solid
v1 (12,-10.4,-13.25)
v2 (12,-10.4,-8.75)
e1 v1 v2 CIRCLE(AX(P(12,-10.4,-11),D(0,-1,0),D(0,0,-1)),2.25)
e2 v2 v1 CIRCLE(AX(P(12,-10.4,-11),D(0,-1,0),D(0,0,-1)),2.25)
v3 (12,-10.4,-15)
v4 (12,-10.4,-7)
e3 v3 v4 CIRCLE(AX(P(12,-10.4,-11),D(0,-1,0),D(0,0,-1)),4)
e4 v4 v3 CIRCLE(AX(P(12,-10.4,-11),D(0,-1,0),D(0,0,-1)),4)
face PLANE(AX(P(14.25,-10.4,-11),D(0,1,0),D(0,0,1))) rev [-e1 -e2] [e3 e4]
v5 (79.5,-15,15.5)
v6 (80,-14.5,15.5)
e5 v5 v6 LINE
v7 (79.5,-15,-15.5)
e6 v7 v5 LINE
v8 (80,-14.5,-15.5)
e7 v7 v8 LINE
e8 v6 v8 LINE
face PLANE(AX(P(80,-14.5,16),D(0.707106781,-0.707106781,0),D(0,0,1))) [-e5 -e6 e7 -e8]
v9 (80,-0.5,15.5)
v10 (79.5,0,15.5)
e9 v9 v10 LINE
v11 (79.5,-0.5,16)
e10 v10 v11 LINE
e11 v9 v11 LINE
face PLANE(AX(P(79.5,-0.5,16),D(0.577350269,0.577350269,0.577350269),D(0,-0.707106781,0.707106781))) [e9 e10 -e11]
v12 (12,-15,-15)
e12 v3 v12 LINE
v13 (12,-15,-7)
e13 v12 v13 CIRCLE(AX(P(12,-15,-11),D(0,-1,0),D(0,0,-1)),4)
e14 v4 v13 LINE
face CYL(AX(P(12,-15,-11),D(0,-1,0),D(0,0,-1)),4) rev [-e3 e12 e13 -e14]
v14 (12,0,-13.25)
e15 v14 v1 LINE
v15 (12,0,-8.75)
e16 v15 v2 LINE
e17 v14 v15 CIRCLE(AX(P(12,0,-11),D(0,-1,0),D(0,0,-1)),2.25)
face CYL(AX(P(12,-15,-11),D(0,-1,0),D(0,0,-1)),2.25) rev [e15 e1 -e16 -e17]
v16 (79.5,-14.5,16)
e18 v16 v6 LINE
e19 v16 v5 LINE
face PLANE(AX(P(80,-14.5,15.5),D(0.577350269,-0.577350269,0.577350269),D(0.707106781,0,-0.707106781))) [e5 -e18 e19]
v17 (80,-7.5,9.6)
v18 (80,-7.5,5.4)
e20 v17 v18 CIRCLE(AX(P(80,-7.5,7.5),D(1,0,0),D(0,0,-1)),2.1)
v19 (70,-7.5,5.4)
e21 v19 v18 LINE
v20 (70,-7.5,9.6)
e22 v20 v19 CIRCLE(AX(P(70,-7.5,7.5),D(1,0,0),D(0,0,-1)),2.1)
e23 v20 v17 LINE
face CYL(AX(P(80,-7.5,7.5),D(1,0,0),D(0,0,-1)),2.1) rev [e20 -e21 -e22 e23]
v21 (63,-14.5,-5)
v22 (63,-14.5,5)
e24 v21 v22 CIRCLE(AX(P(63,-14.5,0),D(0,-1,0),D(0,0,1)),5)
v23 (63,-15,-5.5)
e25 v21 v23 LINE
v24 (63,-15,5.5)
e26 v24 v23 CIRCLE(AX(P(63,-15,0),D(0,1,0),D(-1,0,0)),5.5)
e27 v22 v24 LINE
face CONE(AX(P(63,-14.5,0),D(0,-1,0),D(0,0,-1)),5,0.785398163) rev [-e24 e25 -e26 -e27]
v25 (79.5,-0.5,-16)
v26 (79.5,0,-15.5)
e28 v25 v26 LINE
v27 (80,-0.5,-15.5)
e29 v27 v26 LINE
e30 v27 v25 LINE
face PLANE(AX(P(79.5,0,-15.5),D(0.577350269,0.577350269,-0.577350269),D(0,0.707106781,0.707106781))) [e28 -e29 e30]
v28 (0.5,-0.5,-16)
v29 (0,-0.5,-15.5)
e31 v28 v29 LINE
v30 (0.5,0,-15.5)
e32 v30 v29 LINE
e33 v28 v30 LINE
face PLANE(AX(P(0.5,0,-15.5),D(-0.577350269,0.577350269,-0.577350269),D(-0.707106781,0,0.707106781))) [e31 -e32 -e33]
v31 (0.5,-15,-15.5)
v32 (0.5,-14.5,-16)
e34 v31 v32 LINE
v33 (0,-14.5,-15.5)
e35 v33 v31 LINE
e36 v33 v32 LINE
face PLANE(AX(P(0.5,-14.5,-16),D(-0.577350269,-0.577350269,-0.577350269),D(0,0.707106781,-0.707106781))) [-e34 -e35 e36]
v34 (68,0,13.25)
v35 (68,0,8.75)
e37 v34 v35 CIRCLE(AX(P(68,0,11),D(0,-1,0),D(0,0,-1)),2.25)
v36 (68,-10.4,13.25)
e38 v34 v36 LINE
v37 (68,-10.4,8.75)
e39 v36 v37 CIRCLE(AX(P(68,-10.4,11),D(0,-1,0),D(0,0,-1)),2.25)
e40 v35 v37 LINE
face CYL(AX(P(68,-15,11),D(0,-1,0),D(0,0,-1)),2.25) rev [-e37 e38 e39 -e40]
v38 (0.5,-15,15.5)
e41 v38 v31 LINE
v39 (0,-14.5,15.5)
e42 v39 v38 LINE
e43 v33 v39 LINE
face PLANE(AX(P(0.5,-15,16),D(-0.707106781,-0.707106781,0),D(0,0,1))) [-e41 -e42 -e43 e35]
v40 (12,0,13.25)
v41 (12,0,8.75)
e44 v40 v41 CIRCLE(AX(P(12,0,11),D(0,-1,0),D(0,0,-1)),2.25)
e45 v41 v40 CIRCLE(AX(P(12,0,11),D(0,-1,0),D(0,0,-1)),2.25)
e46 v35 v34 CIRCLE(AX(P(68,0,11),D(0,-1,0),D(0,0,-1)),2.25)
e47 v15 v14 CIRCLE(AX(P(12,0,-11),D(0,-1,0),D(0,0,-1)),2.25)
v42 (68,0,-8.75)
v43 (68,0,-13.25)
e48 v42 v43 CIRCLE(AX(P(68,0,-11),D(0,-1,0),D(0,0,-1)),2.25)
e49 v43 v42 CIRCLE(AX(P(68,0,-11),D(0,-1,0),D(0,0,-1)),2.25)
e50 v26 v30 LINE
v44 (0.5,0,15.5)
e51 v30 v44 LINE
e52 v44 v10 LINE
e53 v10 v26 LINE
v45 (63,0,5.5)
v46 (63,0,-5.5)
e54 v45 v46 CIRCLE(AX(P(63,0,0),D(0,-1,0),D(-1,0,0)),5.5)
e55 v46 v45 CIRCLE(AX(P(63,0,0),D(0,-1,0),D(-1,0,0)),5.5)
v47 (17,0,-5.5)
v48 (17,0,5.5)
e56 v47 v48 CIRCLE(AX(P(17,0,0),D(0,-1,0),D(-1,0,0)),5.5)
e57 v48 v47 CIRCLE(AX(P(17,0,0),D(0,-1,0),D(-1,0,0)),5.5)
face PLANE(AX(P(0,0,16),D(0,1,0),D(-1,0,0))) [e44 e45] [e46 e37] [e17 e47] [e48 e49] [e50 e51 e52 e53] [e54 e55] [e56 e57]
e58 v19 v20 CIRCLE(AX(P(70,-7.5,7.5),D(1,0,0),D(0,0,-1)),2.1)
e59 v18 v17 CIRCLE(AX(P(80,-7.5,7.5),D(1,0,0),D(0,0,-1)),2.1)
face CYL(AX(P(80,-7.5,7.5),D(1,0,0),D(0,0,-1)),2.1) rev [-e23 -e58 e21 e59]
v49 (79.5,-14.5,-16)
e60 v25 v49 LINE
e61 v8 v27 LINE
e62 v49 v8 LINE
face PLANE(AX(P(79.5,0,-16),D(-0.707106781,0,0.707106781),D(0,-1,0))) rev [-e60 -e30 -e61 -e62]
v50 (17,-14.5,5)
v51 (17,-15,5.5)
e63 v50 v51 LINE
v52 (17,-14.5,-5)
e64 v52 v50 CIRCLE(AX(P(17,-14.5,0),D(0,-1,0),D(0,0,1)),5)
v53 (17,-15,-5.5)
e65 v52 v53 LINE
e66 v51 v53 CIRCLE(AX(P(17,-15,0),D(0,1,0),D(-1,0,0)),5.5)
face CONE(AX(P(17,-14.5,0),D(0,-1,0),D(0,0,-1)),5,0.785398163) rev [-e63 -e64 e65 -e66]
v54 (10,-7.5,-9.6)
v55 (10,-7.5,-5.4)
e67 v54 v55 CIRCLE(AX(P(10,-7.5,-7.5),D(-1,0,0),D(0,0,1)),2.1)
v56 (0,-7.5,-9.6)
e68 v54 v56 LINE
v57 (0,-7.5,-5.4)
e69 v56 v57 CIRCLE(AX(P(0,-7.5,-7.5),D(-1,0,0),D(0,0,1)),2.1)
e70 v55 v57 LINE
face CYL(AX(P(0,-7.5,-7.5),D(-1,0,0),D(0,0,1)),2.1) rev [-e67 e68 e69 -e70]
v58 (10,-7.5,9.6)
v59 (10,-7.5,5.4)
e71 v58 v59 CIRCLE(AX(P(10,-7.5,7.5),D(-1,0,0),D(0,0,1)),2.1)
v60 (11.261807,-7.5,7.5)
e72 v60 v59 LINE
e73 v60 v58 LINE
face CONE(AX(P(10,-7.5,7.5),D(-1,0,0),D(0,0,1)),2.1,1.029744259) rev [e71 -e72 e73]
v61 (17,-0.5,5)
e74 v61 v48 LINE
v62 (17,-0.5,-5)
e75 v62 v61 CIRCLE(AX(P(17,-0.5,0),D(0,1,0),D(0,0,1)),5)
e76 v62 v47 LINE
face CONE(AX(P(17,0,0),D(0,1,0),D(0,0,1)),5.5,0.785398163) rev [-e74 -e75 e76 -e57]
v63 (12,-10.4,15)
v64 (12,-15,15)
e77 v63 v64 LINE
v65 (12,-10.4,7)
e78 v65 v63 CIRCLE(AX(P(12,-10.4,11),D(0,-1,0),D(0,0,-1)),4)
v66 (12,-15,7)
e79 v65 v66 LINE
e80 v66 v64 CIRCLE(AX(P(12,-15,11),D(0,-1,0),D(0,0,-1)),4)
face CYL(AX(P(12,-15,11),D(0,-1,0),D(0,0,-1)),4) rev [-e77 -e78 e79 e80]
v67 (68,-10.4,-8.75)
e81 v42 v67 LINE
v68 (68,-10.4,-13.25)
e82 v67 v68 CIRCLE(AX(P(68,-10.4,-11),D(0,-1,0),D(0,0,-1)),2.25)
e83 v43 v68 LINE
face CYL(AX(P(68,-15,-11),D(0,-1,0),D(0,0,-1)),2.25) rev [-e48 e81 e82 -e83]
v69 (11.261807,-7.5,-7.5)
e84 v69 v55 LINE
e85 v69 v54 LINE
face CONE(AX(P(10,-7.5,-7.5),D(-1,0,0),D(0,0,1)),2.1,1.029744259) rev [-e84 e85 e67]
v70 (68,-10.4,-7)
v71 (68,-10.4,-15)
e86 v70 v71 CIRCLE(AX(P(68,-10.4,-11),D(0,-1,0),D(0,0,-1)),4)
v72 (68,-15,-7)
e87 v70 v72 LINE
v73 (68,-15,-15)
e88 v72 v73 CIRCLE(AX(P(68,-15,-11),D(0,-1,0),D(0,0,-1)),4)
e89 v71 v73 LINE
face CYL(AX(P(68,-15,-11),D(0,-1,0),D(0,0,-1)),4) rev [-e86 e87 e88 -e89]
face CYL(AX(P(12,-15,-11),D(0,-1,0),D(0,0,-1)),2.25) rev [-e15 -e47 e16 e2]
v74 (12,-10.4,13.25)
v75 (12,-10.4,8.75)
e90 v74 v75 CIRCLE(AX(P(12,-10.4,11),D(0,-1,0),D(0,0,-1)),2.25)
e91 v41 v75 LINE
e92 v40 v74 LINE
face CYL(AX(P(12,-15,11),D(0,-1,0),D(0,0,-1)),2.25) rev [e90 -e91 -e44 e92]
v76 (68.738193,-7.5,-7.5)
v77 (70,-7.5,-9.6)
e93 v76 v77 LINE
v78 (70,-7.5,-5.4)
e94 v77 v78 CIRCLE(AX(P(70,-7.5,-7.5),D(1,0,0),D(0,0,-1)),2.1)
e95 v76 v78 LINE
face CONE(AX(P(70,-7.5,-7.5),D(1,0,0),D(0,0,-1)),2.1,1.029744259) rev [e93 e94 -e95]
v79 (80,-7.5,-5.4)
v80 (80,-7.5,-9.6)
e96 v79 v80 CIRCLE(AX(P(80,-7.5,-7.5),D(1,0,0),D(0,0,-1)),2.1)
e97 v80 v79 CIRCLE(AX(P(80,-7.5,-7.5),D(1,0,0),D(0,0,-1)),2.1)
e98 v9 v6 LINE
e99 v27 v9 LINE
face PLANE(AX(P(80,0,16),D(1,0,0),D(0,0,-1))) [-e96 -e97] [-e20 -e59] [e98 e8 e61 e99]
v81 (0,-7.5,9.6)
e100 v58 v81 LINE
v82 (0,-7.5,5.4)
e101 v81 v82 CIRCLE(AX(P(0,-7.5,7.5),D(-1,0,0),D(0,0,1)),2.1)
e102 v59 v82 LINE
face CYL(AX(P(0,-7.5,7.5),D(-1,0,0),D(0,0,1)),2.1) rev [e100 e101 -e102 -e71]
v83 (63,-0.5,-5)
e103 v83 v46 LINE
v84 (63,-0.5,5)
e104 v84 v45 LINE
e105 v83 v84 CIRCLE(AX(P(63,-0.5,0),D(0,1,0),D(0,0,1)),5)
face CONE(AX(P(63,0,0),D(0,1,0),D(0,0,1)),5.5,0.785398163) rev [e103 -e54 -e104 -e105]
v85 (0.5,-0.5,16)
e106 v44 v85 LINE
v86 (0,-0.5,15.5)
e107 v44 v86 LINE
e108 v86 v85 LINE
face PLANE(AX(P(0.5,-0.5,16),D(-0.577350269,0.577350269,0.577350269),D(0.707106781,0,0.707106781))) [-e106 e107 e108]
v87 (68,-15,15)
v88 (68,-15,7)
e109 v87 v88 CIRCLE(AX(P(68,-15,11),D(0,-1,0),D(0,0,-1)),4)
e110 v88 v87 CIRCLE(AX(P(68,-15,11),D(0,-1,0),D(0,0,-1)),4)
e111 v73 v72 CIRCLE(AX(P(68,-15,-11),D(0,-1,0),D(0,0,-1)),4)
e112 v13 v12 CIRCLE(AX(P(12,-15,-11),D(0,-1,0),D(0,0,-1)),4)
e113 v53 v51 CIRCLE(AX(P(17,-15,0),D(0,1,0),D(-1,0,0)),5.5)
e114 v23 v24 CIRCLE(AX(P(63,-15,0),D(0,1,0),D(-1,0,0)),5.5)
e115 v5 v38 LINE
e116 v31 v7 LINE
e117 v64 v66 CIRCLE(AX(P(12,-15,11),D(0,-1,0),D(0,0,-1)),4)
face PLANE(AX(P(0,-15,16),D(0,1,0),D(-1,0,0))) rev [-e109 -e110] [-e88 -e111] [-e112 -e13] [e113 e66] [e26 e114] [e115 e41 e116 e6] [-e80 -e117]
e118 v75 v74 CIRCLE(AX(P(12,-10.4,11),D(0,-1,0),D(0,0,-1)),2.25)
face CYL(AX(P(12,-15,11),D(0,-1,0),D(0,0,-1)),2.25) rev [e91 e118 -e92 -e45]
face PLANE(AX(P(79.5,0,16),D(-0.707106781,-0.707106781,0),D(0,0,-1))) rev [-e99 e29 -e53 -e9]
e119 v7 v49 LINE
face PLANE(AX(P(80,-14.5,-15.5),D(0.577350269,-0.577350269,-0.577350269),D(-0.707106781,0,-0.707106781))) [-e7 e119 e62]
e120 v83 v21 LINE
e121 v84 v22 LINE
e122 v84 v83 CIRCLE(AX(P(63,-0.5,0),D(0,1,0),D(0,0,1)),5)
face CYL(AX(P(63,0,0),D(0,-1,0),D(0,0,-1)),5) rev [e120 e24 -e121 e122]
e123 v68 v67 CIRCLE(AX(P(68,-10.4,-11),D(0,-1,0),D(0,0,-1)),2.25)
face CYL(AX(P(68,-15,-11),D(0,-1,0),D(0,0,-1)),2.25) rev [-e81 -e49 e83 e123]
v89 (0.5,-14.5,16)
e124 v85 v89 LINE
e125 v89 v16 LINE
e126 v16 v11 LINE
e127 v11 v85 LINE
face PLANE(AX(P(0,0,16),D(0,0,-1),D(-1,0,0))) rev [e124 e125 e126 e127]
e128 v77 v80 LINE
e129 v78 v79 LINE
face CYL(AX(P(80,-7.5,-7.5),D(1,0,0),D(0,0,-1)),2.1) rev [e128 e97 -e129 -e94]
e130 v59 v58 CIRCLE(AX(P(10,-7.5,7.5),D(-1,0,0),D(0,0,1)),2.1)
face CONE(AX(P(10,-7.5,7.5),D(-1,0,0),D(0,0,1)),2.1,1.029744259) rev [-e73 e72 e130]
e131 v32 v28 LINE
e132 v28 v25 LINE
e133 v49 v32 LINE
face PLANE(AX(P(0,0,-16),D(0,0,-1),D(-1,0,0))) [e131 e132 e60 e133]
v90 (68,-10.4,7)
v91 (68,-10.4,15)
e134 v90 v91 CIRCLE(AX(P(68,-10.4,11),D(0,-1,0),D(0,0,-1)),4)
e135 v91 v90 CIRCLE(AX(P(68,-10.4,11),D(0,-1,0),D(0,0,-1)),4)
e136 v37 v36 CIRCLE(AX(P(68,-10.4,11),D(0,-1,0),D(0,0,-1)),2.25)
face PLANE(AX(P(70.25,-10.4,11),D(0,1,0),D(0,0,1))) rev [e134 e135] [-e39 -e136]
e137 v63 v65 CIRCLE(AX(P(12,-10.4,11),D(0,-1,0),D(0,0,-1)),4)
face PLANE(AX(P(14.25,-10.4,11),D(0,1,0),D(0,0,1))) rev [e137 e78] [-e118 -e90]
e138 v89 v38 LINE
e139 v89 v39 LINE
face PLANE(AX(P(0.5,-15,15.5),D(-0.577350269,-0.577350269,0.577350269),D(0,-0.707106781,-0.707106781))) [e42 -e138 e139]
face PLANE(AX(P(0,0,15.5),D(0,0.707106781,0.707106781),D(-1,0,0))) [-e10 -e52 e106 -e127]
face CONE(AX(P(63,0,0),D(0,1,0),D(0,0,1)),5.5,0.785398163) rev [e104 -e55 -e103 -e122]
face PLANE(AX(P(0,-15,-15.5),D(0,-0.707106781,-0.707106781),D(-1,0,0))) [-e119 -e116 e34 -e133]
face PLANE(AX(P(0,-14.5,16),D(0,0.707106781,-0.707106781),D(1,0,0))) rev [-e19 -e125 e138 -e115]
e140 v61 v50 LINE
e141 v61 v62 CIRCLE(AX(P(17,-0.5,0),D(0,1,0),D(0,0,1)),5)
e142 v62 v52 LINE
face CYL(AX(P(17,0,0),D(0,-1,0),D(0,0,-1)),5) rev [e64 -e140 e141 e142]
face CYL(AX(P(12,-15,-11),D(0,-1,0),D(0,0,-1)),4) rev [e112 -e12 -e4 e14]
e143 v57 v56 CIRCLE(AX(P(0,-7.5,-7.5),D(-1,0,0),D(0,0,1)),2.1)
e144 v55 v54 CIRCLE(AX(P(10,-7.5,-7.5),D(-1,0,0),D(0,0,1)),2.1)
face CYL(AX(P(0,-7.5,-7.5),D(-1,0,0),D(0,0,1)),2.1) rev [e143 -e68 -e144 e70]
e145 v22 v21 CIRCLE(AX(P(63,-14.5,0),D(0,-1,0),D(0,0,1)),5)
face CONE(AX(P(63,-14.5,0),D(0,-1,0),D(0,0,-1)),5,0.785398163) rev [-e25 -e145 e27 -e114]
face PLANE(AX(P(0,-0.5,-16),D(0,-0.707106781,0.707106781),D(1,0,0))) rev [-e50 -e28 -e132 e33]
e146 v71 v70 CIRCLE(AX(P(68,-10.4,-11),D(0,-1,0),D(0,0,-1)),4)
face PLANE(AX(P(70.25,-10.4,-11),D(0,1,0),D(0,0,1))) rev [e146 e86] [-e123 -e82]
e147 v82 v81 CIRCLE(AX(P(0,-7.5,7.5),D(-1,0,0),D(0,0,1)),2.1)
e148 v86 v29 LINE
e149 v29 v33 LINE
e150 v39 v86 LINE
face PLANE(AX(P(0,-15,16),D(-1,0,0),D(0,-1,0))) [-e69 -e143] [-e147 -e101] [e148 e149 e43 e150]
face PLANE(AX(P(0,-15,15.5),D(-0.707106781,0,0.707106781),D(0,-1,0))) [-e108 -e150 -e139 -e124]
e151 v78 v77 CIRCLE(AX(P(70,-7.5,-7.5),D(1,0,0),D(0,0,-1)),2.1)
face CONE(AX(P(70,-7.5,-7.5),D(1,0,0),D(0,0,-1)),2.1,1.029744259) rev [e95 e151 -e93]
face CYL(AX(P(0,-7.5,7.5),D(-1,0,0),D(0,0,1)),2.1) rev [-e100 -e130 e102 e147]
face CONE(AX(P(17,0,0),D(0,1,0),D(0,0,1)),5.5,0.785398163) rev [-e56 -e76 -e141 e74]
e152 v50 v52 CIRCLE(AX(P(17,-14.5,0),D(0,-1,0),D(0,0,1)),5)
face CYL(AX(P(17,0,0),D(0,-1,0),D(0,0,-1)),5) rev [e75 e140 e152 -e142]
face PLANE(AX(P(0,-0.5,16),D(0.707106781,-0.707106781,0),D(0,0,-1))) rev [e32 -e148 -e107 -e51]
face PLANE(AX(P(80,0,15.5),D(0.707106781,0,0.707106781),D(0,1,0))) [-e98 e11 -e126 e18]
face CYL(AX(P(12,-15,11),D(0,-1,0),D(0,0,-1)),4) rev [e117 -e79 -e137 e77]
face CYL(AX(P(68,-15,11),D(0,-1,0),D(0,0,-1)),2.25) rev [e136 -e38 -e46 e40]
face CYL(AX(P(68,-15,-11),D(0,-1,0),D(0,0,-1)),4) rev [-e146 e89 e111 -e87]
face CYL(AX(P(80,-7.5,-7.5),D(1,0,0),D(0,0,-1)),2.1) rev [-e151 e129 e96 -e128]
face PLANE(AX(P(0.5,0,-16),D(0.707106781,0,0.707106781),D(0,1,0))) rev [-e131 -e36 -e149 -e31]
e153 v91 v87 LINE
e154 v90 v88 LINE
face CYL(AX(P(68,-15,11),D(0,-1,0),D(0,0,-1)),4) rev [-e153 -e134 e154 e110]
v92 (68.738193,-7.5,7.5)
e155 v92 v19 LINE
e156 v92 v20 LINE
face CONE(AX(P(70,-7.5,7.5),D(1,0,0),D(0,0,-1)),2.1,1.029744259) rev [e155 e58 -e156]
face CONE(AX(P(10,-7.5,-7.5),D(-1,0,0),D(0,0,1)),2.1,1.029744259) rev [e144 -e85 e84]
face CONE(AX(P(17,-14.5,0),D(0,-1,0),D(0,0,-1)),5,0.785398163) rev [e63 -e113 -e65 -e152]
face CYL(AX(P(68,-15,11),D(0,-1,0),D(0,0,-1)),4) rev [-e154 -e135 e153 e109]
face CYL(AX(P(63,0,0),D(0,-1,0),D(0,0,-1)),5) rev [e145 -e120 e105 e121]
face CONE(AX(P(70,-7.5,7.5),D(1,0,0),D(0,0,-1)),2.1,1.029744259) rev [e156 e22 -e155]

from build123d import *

# Parameters (mm, degrees)
SKETCH1_W                                            = 80
SKETCH1_H                                            = 15
EXTRUDE_THIN1_DEPTH                                  = 16
HOLE_SIZE_BY_SOCKET_HEAD_CAP_SCREW_TYPE1_D           = 4.5
HOLE_SIZE_BY_SOCKET_HEAD_CAP_SCREW_TYPE1_CBORE_D     = 8
HOLE_SIZE_BY_SOCKET_HEAD_CAP_SCREW_TYPE1_CBORE_DEPTH = 4.6
SKETCH4_R                                            = 5
CUT_EXTRUDE1_DEPTH                                   = 83.95179323
M5_TAPPED_HOLE2_D                                    = 4.2
M5_TAPPED_HOLE2_DEPTH                                = 10
M5_TAPPED_HOLE2_TIP                                  = 1.2618073
M5_TAPPED_HOLE1_D                                    = 4.2
M5_TAPPED_HOLE1_DEPTH                                = 10
M5_TAPPED_HOLE1_TIP                                  = 1.2618073
CHAMFER1_SIZE                                        = 0.5


with BuildPart() as part:
    # Sketch1 → Extrude-Thin1 (new, symmetric)
    with BuildSketch(Plane.XY):
        with Locations((40, -7.5)):
            Rectangle(SKETCH1_W, SKETCH1_H)
    extrude(amount=EXTRUDE_THIN1_DEPTH, both=True)

    # Hole size by socket head cap screw type1 (through all)
    with Locations(Plane(origin=(0, -15, 0), x_dir=(-1, 0, 0), z_dir=(0, -1, 0))):
        with Locations((-68, -11), (-68, 11), (-12, -11), (-12, 11)):
            CounterBoreHole(HOLE_SIZE_BY_SOCKET_HEAD_CAP_SCREW_TYPE1_D / 2, HOLE_SIZE_BY_SOCKET_HEAD_CAP_SCREW_TYPE1_CBORE_D / 2, HOLE_SIZE_BY_SOCKET_HEAD_CAP_SCREW_TYPE1_CBORE_DEPTH)

    # Sketch4 → Cut-Extrude1 (cut, through all)
    with BuildSketch(Plane.XZ.offset(15)):
        with Locations(Location((17, 0, 0), (0, 0, 270))):
            Circle(SKETCH4_R)
        with Locations(Location((63, 0, 0), (0, 0, 270))):
            Circle(SKETCH4_R)
    extrude(amount=-CUT_EXTRUDE1_DEPTH, mode=Mode.SUBTRACT)

    # M5 Tapped Hole2
    with Locations(Plane(origin=(80, 0, 0), x_dir=(0, 0, -1), z_dir=(1, 0, 0))):
        with Locations((-7.5, -7.5), (7.5, -7.5)):
            Hole(M5_TAPPED_HOLE2_D / 2, depth=M5_TAPPED_HOLE2_DEPTH)
            with Locations((0, 0, -(M5_TAPPED_HOLE2_DEPTH + M5_TAPPED_HOLE2_TIP / 2))):  # 118° drill point
                Cone(0, M5_TAPPED_HOLE2_D / 2, M5_TAPPED_HOLE2_TIP, mode=Mode.SUBTRACT)

    # M5 Tapped Hole1
    with Locations(Plane(origin=(0, -24.315194206, 11.709083439), x_dir=(0, 0, 1), z_dir=(-1, 0, 0))):
        with Locations((-19.209083439, 16.815194206), (-4.209083439, 16.815194206)):
            Hole(M5_TAPPED_HOLE1_D / 2, depth=M5_TAPPED_HOLE1_DEPTH)
            with Locations((0, 0, -(M5_TAPPED_HOLE1_DEPTH + M5_TAPPED_HOLE1_TIP / 2))):  # 118° drill point
                Cone(0, M5_TAPPED_HOLE1_D / 2, M5_TAPPED_HOLE1_TIP, mode=Mode.SUBTRACT)

    # Chamfer1
    chamfer1_edges = [part.edges().sort_by_distance(p)[0] for p in [
        (40, 0, 16),
        (0, -7.5, 16),
        (0, -7.5, -16),
        (40, -15, 16),
        (40, 0, -16),
        (17, 0, 5),
        (17, -15, 5),
        (80, -7.5, -16),
        (63, 0, 5),
        (63, -15, 5),
        (40, -15, -16),
        (0, -15, 0),
        (0, 0, 0),
        (80, 0, 0),
        (80, -15, 0),
        (80, -7.5, 16),
    ]]
    chamfer(chamfer1_edges, length=CHAMFER1_SIZE)


solid = part.part
